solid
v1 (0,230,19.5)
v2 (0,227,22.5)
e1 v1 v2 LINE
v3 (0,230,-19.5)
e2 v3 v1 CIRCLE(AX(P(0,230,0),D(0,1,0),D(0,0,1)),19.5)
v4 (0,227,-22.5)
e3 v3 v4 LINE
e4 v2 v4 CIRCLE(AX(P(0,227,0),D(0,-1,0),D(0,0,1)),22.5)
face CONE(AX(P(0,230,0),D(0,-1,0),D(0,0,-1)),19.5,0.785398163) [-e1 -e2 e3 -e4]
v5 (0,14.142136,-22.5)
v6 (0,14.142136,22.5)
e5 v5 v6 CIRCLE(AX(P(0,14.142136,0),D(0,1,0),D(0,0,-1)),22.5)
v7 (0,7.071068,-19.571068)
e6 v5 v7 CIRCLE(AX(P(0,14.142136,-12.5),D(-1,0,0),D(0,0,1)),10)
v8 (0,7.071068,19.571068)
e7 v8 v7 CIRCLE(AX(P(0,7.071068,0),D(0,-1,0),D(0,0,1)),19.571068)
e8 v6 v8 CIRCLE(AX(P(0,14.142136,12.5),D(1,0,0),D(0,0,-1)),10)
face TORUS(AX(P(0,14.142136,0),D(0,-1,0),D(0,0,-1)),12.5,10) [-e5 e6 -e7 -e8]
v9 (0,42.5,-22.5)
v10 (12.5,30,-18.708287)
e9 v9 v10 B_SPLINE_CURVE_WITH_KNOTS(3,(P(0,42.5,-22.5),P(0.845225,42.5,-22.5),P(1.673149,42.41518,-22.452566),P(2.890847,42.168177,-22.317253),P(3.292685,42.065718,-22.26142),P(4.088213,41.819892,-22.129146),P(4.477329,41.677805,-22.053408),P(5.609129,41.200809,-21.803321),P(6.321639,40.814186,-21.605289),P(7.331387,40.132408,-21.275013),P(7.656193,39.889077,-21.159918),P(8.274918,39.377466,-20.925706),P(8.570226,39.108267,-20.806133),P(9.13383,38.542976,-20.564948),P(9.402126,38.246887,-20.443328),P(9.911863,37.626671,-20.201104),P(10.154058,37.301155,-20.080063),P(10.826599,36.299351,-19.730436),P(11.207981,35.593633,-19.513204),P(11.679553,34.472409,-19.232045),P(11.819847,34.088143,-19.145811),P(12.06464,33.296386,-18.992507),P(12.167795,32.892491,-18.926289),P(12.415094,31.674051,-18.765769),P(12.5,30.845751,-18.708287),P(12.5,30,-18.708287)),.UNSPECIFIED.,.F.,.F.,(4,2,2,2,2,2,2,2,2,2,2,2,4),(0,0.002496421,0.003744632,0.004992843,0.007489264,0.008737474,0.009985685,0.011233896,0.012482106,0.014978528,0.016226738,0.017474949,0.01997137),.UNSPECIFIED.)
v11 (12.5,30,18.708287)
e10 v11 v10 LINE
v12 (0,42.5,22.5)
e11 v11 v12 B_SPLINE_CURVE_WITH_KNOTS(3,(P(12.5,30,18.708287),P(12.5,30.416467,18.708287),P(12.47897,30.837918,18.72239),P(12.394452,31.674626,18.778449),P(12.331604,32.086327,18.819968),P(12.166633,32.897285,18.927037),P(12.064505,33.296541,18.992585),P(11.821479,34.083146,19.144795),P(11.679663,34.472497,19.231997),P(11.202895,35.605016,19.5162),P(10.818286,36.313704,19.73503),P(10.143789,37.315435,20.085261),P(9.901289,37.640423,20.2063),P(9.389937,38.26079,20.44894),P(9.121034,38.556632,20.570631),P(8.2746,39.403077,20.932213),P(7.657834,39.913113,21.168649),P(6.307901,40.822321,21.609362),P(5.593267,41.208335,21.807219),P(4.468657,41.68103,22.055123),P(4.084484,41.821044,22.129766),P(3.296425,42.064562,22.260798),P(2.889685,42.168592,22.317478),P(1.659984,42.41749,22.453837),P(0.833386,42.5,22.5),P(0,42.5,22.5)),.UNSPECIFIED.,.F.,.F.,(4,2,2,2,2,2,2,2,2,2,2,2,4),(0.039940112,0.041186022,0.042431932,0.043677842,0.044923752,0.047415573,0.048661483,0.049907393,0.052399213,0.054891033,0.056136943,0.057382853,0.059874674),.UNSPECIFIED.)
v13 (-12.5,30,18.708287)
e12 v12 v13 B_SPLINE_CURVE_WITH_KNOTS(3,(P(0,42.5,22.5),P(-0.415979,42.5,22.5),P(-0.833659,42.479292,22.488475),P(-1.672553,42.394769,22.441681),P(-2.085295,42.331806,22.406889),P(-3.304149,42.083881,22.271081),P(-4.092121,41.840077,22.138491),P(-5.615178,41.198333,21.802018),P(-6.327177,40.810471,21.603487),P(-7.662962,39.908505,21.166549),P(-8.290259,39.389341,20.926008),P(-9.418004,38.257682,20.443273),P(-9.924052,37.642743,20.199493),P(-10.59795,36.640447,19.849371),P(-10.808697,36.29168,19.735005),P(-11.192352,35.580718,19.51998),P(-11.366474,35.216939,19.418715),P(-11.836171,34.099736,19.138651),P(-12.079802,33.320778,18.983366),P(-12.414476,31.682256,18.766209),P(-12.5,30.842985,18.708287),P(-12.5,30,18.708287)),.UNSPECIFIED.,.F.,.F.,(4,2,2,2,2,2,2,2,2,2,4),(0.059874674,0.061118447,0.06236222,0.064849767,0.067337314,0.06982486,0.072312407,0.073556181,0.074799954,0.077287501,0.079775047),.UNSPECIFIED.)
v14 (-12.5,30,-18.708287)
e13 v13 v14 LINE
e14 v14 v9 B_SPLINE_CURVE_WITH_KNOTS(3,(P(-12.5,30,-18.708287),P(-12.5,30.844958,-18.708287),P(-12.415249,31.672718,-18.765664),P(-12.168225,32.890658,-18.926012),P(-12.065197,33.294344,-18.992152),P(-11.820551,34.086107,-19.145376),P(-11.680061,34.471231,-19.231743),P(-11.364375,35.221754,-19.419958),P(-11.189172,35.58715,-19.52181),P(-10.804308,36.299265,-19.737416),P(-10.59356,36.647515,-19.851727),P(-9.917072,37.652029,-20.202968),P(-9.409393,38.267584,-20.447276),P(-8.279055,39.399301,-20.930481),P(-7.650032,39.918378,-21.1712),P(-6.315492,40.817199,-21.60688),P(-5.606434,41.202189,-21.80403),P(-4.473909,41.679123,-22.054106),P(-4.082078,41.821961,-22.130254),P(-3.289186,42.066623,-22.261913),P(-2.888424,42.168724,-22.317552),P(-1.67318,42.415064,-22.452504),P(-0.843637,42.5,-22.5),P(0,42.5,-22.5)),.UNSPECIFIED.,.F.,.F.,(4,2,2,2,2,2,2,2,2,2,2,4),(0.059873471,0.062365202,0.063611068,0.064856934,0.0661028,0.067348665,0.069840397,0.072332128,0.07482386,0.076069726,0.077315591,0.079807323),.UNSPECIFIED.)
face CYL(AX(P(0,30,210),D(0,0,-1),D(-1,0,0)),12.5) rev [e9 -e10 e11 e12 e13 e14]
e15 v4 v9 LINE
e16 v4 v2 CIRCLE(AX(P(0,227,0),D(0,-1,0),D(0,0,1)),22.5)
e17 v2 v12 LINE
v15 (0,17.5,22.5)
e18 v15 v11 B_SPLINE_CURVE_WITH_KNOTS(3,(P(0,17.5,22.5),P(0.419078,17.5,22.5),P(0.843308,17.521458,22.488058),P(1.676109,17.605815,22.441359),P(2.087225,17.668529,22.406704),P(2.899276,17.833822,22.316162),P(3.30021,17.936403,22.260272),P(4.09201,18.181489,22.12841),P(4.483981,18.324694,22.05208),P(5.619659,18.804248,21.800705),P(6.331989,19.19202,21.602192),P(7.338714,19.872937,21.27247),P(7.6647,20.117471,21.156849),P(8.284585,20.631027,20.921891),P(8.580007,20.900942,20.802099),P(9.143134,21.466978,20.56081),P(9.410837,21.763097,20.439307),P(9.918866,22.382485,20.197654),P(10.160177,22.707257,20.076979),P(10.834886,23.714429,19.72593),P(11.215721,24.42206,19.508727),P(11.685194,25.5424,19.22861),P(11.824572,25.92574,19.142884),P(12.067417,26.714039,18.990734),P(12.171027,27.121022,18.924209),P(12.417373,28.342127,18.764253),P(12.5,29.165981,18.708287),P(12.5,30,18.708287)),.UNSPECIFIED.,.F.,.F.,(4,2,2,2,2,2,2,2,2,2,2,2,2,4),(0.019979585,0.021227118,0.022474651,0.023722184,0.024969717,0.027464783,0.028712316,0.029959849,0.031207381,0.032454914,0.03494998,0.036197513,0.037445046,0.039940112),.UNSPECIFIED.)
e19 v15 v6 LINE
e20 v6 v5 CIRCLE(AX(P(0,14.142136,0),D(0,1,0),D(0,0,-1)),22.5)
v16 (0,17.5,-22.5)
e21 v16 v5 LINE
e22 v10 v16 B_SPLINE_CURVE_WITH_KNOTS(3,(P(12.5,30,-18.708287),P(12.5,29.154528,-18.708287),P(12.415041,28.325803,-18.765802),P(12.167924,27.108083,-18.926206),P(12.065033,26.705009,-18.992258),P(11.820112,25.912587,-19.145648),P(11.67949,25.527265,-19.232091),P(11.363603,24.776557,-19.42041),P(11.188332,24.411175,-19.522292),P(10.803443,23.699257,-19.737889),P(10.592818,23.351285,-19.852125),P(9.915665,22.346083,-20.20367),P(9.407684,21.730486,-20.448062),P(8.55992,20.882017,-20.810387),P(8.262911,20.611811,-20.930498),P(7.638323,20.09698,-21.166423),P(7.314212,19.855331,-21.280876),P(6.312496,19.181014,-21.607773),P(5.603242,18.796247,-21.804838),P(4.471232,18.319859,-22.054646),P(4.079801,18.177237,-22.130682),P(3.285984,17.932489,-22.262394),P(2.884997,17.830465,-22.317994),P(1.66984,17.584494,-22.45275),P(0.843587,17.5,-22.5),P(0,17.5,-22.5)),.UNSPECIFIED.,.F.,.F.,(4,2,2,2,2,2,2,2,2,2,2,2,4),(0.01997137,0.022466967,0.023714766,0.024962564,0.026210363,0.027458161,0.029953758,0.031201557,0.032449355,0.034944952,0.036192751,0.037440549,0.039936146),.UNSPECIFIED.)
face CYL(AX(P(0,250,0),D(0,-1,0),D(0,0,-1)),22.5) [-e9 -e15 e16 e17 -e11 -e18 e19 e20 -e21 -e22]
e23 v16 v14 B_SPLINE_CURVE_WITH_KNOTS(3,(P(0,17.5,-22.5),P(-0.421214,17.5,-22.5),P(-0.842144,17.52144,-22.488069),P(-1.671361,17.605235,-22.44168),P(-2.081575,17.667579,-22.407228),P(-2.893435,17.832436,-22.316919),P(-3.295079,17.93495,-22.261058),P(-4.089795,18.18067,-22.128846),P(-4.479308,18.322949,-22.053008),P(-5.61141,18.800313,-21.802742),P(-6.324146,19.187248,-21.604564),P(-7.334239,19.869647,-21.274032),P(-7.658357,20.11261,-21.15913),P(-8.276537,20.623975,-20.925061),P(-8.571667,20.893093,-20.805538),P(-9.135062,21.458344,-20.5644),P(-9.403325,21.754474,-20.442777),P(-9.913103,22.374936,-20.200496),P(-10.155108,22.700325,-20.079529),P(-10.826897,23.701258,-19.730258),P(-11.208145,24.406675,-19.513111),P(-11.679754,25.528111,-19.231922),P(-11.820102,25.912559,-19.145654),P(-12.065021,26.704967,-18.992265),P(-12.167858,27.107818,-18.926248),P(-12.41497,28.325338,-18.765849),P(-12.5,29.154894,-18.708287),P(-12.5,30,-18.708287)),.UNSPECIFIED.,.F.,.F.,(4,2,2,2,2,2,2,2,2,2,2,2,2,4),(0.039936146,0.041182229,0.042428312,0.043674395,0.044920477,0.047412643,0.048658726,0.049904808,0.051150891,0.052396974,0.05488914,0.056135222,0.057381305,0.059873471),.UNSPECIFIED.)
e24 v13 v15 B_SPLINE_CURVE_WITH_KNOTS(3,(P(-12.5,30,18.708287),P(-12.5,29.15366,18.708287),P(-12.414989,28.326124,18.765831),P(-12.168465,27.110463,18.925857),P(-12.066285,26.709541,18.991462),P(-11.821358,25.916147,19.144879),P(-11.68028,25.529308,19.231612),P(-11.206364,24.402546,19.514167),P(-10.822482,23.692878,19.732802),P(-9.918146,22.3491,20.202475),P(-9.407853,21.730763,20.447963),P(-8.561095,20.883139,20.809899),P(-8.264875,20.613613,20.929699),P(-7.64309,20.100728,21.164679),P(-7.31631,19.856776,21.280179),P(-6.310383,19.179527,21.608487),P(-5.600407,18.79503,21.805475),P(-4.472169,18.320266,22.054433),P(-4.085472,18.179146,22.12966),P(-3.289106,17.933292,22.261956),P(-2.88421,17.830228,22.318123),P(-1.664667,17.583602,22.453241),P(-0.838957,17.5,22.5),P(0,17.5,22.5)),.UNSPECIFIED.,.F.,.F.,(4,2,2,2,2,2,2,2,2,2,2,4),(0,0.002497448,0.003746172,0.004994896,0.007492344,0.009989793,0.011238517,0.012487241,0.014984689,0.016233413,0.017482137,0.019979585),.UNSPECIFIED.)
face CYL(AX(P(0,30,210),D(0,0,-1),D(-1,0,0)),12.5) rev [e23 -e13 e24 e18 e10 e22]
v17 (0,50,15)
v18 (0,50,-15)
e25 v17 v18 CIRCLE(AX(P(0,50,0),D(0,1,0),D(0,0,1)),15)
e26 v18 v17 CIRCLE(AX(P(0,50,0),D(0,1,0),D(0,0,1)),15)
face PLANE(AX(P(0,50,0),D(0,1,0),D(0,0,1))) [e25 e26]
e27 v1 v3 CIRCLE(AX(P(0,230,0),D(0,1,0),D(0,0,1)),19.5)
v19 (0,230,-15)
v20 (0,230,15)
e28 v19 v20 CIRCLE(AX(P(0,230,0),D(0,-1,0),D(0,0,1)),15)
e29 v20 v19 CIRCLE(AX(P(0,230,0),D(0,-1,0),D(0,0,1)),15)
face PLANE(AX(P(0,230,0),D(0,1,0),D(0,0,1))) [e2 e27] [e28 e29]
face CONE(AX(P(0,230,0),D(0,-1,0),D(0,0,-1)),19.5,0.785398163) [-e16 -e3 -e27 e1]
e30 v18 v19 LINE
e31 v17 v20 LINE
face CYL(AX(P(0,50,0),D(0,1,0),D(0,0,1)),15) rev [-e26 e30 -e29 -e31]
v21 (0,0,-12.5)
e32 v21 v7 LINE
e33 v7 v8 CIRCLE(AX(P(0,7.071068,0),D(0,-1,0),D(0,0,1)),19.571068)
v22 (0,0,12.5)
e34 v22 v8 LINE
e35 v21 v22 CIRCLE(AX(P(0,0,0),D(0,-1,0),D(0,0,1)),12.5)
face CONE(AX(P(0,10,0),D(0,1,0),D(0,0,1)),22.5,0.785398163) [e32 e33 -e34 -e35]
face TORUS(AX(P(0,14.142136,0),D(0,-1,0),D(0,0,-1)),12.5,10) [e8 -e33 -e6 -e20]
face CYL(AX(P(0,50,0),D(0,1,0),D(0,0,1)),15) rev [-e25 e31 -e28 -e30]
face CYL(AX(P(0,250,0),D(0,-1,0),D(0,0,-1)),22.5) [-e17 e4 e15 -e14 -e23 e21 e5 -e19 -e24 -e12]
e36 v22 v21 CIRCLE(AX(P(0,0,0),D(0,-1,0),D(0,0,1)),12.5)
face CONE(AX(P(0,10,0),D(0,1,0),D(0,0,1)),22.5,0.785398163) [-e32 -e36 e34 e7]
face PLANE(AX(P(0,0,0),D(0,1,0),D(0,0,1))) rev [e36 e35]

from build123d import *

# Parameters (mm, degrees)
SKETCH_1_R              = 22.5
EXTRUDE_1_DEPTH         = 250
SKETCH_2_R              = 15
CUT_EXTRUDE_1_DEPTH     = 200
CUT_EXTRUDE2_DEPTH      = 210
CUT_EXTRUDE2_DEPTH_BACK = 210
SKETCH_3_R              = 12.5
SKETCH_4_R              = 53.120468805
CUT_EXTRUDE3_DEPTH      = 20
CHAMFER1_SIZE           = 10
CHAMFER2_SIZE           = 3
FILLET1_R               = 10


with BuildPart() as part:
    # 草图1 → 凸台-拉伸1 (new body)
    with BuildSketch(Plane(origin=(0, 0, 0), x_dir=(1, 0, 0), z_dir=(0, 1, 0))):
        with Locations(Location((0, 0, 0), (0, 0, 270))):
            Circle(SKETCH_1_R)
    extrude(amount=EXTRUDE_1_DEPTH)

    # 草图2 → 切除-拉伸1 (cut)
    with BuildSketch(Plane(origin=(0, 250, 0), x_dir=(1, 0, 0), z_dir=(0, 1, 0))):
        with Locations(Location((0, 0, 0), (0, 0, 270))):
            Circle(SKETCH_2_R)
    extrude(amount=-CUT_EXTRUDE_1_DEPTH, mode=Mode.SUBTRACT)

    # 草图3 → Cut-Extrude2 (cut, two sides: drawn at the far end of the back side and taken through both)
    with BuildSketch(Plane.XY.offset(-CUT_EXTRUDE2_DEPTH_BACK)):
        with Locations(Location((0, 30, 0), (0, 0, 90))):
            Circle(SKETCH_3_R)
    extrude(amount=CUT_EXTRUDE2_DEPTH + CUT_EXTRUDE2_DEPTH_BACK, mode=Mode.SUBTRACT)

    # 草图4 → Cut-Extrude3 (cut)
    with BuildSketch(Plane(origin=(0, 250, 0), x_dir=(1, 0, 0), z_dir=(0, 1, 0))):
        Circle(SKETCH_4_R)
    extrude(amount=-CUT_EXTRUDE3_DEPTH, mode=Mode.SUBTRACT)

    # Chamfer1
    chamfer1_edges = [part.edges().sort_by_distance(p)[0] for p in [
        (0, 0, -22.5),
    ]]
    chamfer(chamfer1_edges, length=CHAMFER1_SIZE)

    # Chamfer2
    chamfer2_edges = [part.edges().sort_by_distance(p)[0] for p in [
        (0, 230, -22.5),
    ]]
    chamfer(chamfer2_edges, length=CHAMFER2_SIZE)

    # Fillet1
    fillet1_edges = [part.edges().sort_by_distance(p)[0] for p in [
        (0, 10, -22.5),
    ]]
    fillet(fillet1_edges, radius=FILLET1_R)


solid = part.part
